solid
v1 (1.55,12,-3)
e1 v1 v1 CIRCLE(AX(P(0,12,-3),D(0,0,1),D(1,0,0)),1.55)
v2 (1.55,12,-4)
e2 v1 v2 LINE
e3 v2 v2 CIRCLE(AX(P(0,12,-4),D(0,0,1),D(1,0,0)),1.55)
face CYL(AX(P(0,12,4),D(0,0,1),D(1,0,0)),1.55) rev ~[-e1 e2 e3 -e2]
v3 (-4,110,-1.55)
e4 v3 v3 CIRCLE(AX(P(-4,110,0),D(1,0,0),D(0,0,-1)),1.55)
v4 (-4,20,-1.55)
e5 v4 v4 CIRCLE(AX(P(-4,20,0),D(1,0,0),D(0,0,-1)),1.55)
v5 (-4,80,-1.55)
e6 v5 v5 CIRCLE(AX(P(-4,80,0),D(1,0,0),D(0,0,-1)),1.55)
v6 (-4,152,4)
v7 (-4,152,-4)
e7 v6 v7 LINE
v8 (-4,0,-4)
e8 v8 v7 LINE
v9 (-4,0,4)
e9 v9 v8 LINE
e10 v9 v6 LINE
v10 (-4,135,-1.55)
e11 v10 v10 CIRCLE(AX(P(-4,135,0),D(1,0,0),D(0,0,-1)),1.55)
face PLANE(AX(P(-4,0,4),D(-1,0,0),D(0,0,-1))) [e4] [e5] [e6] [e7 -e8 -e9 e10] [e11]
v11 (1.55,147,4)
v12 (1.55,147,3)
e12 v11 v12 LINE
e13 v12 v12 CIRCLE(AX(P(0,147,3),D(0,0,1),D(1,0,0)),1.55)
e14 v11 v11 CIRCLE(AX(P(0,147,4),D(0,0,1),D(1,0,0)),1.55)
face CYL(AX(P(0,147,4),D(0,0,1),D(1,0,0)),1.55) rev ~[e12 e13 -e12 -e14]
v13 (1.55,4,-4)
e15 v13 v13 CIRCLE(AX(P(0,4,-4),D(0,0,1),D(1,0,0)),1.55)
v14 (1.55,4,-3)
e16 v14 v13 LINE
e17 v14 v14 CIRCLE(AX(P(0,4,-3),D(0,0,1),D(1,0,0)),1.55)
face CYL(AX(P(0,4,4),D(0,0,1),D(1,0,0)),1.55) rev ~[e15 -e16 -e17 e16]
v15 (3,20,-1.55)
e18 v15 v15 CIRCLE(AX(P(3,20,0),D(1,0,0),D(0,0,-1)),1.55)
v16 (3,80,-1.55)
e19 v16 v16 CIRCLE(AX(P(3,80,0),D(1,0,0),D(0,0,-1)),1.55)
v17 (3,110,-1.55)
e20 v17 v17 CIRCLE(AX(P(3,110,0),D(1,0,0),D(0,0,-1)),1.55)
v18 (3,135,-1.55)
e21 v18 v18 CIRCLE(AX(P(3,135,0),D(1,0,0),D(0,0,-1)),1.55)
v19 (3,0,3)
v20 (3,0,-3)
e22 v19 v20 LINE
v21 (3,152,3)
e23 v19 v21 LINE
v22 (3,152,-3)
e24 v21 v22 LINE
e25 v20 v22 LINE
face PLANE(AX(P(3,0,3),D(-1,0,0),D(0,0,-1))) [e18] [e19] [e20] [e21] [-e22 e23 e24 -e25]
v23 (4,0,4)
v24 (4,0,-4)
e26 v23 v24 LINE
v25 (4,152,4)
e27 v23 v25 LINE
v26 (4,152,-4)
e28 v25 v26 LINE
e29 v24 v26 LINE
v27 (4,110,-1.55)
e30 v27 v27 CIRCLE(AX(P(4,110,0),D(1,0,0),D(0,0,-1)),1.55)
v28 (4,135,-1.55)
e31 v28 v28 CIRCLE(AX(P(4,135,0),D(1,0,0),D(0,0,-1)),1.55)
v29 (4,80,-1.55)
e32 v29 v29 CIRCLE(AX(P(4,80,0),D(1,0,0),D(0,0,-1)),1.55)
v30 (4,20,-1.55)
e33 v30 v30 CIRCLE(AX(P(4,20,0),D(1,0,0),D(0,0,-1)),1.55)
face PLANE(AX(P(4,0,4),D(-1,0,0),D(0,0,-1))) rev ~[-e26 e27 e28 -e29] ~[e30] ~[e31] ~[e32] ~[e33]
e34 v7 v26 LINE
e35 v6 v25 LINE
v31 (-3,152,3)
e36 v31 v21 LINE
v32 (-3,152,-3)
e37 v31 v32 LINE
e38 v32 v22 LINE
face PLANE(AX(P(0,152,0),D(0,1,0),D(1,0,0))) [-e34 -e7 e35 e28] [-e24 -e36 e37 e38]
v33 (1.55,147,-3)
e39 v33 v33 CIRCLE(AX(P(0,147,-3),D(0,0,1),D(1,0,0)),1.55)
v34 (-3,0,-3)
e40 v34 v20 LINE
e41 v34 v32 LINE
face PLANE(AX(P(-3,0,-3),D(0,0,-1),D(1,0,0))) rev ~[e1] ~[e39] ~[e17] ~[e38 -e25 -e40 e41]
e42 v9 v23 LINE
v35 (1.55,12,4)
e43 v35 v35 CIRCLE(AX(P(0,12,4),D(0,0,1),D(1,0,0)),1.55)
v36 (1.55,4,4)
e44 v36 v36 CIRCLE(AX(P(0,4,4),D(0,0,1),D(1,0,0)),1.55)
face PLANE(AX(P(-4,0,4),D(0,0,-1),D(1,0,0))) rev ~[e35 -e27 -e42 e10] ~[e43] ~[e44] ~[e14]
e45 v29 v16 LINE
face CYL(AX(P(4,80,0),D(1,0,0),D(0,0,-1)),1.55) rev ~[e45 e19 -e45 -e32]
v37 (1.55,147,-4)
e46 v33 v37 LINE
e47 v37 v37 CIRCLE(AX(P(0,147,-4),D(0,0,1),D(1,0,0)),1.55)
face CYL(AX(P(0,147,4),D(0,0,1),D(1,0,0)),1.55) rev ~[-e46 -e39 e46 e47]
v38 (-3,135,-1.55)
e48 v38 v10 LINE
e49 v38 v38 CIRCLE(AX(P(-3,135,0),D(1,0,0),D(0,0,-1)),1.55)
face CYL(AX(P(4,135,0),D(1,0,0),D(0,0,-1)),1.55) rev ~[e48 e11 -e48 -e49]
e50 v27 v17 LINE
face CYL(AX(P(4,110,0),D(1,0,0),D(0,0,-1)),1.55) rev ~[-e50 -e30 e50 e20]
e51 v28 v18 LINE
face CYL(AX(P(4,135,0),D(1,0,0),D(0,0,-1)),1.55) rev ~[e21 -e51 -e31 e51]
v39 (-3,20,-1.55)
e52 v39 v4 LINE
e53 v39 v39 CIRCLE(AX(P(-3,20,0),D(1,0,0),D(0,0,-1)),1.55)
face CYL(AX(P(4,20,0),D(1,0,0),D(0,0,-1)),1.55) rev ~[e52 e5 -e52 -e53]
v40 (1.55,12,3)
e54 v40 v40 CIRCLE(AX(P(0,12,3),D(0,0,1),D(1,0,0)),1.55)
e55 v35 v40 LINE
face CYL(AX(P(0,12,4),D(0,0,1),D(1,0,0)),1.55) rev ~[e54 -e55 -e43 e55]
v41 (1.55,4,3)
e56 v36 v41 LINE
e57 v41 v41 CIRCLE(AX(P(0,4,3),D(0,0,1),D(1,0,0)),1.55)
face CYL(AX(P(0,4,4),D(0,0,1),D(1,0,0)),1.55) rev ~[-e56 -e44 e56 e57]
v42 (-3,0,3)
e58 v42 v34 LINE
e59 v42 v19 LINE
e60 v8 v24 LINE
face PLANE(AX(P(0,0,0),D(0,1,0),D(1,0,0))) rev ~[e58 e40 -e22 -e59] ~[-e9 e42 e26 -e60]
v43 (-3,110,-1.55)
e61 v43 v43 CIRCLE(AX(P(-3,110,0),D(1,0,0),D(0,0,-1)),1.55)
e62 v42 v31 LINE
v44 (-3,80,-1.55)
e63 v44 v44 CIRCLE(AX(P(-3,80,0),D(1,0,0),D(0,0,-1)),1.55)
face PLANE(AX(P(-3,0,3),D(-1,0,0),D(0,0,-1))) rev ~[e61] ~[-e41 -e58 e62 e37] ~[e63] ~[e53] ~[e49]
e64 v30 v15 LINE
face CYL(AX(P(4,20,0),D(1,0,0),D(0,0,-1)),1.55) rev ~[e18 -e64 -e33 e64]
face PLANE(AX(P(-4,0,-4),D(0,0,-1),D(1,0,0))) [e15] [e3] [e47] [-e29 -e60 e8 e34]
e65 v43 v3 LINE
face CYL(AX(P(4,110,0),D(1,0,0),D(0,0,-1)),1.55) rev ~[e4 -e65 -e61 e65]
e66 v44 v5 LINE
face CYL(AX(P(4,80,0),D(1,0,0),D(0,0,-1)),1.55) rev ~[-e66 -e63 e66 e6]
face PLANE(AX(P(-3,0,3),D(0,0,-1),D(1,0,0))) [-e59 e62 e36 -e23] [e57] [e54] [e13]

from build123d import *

# Parameters (mm, degrees)
SKETCH_1_W          = 8
SKETCH_1_H          = 8
SKETCH_1_W_2        = 6
SKETCH_1_H_2        = 6
EXTRUDE_1_DEPTH     = 152
SKETCH_2_R          = 1.55
CUT_EXTRUDE_1_DEPTH = 153.262930485
SKETCH_3_R          = 1.55
CUT_EXTRUDE_2_DEPTH = 153.262930485


with BuildPart() as part:
    # 草图1 → 凸台-拉伸1 (new body)
    with BuildSketch(Plane(origin=(0, 0, 0), x_dir=(1, 0, 0), z_dir=(0, 1, 0))):
        Rectangle(SKETCH_1_W, SKETCH_1_H)
        Rectangle(SKETCH_1_W_2, SKETCH_1_H_2, mode=Mode.SUBTRACT)
    extrude(amount=EXTRUDE_1_DEPTH)

    # 草图2 → 切除-拉伸1 (cut, through all)
    with BuildSketch(Plane.XY.offset(4)):
        with Locations((0, 147)):
            Circle(SKETCH_2_R)
        with Locations((0, 4)):
            Circle(SKETCH_2_R)
        with Locations((0, 12)):
            Circle(SKETCH_2_R)
    extrude(amount=-CUT_EXTRUDE_1_DEPTH, mode=Mode.SUBTRACT)

    # 草图3 → 切除-拉伸2 (cut, through all)
    with BuildSketch(Plane(origin=(4, 0, 0), x_dir=(0, 0, -1), z_dir=(1, 0, 0))):
        with Locations((0, 135)):
            Circle(SKETCH_3_R)
        with Locations((0, 20)):
            Circle(SKETCH_3_R)
        with Locations((0, 110)):
            Circle(SKETCH_3_R)
        with Locations((0, 80)):
            Circle(SKETCH_3_R)
    extrude(amount=-CUT_EXTRUDE_2_DEPTH, mode=Mode.SUBTRACT)


solid = part.part
